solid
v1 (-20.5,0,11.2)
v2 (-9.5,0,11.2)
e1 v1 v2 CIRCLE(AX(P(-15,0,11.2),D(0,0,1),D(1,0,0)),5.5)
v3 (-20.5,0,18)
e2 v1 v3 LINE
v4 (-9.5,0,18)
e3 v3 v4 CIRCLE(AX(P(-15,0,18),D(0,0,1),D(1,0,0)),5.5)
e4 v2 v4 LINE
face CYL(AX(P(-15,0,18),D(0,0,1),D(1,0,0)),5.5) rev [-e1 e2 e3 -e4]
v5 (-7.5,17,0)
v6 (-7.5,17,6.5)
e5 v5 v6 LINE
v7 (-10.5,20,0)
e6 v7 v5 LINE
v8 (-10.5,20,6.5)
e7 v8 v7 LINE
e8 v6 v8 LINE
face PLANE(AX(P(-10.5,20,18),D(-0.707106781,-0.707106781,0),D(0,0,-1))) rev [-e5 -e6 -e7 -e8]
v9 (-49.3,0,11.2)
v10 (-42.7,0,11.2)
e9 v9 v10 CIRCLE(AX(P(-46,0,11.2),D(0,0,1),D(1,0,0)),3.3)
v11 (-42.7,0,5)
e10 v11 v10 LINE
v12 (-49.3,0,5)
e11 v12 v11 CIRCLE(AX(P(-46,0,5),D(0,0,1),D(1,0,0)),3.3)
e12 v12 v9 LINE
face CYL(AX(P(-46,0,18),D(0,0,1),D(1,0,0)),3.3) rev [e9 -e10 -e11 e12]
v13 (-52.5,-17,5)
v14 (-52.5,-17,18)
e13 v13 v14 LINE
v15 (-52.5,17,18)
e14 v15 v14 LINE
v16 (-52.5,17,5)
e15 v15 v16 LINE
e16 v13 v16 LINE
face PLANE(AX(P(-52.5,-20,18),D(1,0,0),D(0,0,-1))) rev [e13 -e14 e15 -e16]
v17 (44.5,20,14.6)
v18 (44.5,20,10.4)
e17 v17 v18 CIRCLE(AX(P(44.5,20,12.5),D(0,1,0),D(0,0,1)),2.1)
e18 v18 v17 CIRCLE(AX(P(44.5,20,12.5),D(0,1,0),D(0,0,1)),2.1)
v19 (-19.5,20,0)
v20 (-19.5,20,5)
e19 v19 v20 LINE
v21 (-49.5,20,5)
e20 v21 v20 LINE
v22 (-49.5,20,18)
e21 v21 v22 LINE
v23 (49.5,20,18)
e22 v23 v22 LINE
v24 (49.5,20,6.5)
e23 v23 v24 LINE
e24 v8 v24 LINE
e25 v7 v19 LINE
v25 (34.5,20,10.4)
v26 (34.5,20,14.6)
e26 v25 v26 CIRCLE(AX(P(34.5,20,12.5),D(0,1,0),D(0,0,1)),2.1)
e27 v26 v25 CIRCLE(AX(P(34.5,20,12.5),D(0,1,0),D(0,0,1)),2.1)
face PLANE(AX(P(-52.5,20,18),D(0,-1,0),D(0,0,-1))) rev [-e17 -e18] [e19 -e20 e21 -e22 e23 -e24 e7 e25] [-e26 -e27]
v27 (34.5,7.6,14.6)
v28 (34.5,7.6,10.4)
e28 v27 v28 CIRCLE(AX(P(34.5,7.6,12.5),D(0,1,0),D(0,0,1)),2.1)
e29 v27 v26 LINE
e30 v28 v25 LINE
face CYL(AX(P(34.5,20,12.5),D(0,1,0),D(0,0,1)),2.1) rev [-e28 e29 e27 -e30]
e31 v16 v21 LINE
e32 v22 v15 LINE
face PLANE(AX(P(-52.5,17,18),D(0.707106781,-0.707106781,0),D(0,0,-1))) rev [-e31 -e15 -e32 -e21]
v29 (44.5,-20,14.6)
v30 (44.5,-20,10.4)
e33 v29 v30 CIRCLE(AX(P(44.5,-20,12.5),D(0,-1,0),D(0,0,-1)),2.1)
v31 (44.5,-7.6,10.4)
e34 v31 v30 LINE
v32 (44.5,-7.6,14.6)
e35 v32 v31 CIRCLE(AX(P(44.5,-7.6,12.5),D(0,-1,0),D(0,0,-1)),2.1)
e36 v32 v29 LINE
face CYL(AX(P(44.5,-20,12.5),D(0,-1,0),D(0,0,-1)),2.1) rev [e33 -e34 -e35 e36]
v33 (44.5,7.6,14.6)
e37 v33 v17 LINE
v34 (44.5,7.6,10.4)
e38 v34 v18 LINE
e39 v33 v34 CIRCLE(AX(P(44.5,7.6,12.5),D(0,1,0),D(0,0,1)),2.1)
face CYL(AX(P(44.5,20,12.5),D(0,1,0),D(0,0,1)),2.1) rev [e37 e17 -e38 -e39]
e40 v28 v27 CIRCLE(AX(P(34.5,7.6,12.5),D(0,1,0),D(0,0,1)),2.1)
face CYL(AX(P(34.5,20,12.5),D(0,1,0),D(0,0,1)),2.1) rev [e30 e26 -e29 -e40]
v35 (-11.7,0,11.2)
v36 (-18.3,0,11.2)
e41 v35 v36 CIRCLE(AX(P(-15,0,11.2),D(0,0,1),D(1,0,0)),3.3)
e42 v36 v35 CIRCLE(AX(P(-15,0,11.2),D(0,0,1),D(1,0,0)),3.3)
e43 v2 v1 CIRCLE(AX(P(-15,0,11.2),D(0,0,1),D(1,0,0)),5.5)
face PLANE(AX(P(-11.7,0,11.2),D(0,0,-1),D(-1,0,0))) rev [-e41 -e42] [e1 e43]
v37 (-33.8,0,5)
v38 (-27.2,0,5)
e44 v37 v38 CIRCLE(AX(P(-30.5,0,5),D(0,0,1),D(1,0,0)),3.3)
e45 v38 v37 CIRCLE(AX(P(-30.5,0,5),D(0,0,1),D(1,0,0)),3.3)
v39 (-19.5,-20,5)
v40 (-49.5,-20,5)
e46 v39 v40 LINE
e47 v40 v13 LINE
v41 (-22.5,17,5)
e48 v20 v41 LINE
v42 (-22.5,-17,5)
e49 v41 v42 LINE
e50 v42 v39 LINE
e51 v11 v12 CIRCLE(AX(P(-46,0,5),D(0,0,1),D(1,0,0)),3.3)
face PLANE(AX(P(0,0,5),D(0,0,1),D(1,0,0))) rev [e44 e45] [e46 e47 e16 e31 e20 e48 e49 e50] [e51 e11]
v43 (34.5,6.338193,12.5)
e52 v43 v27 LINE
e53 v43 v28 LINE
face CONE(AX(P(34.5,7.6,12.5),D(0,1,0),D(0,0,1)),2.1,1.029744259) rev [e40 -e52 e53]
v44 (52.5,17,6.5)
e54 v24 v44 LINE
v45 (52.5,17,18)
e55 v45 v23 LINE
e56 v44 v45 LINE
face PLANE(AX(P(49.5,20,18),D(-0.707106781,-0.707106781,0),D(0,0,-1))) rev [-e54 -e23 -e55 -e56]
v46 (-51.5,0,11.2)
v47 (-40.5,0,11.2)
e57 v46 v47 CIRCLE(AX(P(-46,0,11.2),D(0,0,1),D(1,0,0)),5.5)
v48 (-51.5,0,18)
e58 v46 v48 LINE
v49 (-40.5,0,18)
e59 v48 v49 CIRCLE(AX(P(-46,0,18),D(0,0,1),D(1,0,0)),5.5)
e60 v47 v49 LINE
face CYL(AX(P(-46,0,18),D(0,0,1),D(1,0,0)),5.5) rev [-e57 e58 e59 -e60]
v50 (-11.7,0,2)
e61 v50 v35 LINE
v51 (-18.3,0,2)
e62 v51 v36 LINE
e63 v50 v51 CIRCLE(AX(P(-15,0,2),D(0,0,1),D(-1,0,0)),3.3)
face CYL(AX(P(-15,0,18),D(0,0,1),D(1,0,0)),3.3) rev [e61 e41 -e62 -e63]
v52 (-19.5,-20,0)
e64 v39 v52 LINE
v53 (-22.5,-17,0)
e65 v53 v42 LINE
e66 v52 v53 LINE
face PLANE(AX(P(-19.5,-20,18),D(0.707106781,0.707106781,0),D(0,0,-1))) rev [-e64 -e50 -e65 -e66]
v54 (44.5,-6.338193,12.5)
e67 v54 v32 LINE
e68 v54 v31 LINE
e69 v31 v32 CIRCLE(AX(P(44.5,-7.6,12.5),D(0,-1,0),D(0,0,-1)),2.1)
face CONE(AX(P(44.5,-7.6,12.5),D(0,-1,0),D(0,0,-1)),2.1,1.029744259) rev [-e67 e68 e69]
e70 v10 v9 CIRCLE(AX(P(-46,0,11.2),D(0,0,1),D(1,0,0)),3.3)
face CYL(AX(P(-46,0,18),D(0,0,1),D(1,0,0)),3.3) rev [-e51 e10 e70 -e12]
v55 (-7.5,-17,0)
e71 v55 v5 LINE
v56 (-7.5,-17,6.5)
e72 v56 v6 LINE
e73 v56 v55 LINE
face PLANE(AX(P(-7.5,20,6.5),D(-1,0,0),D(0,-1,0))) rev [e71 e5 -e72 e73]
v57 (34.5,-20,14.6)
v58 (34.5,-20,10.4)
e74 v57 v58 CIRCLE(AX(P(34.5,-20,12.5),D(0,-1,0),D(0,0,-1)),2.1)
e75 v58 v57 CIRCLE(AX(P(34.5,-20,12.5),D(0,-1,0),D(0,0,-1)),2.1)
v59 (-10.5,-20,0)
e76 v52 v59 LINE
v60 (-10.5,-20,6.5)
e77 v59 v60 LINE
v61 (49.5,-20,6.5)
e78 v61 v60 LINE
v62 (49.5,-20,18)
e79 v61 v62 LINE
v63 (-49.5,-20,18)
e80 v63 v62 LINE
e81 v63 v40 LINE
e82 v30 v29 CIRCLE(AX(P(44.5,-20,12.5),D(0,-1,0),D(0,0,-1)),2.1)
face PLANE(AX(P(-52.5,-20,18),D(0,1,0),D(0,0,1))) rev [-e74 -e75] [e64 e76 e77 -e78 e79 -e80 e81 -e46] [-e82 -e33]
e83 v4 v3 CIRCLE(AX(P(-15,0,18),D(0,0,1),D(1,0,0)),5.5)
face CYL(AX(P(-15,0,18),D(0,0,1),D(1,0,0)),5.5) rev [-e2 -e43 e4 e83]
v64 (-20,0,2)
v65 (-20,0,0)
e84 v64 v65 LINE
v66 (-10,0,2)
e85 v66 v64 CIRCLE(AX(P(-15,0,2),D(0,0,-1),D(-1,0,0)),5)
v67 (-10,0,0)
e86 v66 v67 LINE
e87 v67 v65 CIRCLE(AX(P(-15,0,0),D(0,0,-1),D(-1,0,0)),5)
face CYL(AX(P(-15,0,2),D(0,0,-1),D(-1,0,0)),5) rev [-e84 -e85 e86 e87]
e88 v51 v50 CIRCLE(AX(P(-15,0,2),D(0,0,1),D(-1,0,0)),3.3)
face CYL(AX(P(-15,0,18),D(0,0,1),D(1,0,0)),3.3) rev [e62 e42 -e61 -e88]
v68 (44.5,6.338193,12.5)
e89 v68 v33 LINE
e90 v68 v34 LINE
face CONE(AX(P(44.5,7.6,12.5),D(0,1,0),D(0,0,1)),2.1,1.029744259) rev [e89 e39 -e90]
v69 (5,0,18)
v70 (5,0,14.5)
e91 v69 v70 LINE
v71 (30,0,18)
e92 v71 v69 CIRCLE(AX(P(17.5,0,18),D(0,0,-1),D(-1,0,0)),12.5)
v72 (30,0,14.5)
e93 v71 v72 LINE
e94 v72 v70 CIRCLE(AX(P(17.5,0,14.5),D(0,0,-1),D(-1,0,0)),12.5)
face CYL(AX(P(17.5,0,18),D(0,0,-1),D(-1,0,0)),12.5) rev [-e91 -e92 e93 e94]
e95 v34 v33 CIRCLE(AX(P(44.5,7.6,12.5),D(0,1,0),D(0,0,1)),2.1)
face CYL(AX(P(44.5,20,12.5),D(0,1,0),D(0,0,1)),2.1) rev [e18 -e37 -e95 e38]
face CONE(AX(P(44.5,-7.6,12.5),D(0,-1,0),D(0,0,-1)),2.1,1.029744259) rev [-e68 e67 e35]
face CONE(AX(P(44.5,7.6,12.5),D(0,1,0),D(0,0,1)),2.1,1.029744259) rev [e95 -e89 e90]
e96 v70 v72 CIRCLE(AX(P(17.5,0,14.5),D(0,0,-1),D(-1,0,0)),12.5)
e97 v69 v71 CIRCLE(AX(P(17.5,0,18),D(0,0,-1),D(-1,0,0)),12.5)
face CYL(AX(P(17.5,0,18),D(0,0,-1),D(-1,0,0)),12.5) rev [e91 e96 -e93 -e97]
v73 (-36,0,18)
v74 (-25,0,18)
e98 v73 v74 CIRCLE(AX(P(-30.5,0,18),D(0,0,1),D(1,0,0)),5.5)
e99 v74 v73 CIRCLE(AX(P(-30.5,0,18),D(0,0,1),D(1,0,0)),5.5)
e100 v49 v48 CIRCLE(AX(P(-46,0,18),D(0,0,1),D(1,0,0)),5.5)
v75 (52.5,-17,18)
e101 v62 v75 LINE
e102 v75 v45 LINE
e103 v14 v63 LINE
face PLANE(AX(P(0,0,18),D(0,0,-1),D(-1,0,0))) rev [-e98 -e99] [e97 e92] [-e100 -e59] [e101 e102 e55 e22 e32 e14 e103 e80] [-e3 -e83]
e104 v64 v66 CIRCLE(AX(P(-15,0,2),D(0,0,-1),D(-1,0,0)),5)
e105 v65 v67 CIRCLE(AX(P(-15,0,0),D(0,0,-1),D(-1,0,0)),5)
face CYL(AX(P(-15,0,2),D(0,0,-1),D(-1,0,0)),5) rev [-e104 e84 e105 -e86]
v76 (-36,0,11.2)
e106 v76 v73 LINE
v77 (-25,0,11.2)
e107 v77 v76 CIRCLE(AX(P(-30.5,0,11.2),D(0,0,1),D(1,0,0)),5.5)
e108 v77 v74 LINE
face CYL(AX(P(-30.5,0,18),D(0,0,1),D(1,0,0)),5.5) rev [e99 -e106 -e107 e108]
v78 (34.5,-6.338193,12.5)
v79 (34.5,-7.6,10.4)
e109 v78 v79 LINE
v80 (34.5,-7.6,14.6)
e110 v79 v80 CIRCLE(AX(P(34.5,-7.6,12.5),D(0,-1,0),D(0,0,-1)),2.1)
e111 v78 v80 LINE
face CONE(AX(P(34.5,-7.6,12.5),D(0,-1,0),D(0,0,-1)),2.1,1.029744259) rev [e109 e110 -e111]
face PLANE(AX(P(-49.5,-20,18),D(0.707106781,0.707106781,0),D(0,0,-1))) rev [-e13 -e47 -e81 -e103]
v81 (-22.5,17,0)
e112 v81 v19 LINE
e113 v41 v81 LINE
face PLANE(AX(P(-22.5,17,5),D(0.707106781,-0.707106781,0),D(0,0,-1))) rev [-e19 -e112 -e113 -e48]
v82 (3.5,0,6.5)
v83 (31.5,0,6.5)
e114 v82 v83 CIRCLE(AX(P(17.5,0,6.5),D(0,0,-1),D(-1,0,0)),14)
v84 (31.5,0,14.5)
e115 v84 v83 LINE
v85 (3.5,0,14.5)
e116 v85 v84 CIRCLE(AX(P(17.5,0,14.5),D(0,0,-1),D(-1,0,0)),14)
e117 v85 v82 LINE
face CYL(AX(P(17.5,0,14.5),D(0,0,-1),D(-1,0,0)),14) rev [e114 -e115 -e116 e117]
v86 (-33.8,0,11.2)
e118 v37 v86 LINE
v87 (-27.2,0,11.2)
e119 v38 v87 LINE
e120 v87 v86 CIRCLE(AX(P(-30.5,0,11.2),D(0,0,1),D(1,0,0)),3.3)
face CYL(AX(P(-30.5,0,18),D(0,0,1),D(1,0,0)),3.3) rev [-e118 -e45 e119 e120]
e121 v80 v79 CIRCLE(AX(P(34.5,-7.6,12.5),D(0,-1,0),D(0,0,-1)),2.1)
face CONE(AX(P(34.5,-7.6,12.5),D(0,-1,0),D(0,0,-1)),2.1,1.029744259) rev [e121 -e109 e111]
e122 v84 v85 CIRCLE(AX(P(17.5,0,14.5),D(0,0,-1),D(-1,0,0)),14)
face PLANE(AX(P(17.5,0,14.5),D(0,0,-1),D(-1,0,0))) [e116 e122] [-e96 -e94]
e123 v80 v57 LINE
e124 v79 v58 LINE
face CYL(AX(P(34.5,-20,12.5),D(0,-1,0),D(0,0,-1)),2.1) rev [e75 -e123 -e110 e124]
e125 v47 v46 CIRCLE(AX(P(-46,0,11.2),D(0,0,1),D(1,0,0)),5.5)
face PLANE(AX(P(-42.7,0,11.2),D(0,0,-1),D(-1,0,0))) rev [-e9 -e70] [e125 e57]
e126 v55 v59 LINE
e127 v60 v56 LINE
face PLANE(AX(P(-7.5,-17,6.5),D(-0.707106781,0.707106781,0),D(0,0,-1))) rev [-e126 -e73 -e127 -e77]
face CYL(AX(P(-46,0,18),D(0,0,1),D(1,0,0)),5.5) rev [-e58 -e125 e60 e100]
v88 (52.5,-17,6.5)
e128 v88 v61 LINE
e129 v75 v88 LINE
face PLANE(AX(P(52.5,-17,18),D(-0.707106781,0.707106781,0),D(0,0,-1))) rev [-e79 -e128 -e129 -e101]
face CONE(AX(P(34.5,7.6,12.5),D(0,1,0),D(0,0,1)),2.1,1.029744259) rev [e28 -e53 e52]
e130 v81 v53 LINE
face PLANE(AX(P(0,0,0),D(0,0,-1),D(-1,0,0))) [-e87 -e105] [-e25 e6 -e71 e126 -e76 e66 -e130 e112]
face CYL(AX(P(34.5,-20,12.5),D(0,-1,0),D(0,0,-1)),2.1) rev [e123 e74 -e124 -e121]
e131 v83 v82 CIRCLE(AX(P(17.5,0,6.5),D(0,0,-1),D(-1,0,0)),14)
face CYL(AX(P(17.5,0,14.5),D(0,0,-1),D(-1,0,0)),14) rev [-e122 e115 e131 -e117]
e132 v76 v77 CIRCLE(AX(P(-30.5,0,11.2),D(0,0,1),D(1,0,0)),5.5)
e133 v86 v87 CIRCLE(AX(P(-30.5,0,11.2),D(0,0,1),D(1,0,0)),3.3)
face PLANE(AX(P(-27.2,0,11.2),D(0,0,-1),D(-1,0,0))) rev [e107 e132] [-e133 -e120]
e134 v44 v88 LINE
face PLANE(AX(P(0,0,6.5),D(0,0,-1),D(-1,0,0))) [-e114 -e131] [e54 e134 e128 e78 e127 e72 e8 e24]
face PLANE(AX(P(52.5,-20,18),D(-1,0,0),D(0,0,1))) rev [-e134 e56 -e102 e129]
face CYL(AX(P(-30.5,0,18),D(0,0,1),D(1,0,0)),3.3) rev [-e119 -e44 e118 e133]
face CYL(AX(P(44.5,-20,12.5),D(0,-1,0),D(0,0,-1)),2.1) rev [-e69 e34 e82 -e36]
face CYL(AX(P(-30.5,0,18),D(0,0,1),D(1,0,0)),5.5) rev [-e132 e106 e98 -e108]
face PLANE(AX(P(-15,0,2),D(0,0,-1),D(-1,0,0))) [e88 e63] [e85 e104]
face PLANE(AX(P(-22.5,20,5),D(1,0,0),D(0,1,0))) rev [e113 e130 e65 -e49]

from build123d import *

# Parameters (mm, degrees)
SKETCH_1_W                  = 105
SKETCH_1_H                  = 40
EXTRUDE_1_DEPTH             = 18
SKETCH_2_W                  = 30
SKETCH_2_H                  = 40
CUT_EXTRUDE_1_DEPTH         = 5
SKETCH_3_W                  = 60
SKETCH_3_H                  = 40
CUT_EXTRUDE_2_DEPTH         = 6.5
HOLE_WIZARD_1_D             = 6.6
HOLE_WIZARD_1_CBORE_D       = 11
HOLE_WIZARD_1_CBORE_DEPTH   = 6.8
SKETCH_6_R                  = 5
CUT_EXTRUDE_3_DEPTH         = 2
SKETCH_7_R                  = 14
CUT_EXTRUDE_4_DEPTH         = 8
SKETCH_8_R                  = 12.5
CUT_EXTRUDE_5_DEPTH         = 59.021547722
CHAMFER_1_SIZE              = 3
HOLE_WIZARD_M5_1_AT_2_COUNT = 2
HOLE_WIZARD_M5_1_AT_2_PITCH = 10


with BuildPart() as part:
    # 草图1 → 凸台-拉伸1 (new body)
    with BuildSketch(Plane.XY):
        Rectangle(SKETCH_1_W, SKETCH_1_H)
    extrude(amount=EXTRUDE_1_DEPTH)

    # 草图2 → 切除-拉伸1 (cut)
    with BuildSketch(Plane(origin=(0, 0, 0), x_dir=(-1, 0, 0), z_dir=(0, 0, -1))):
        with Locations((37.5, 0)):
            Rectangle(SKETCH_2_W, SKETCH_2_H)
    extrude(amount=-CUT_EXTRUDE_1_DEPTH, mode=Mode.SUBTRACT)

    # 草图3 → 切除-拉伸2 (cut)
    with BuildSketch(Plane(origin=(0, 0, 0), x_dir=(-1, 0, 0), z_dir=(0, 0, -1))):
        with Locations((-22.5, 0)):
            Rectangle(SKETCH_3_W, SKETCH_3_H)
    extrude(amount=-CUT_EXTRUDE_2_DEPTH, mode=Mode.SUBTRACT)

    # 打孔尺寸(%根据)内六角圆柱头螺钉的类型1 (through all)
    with Locations(Plane.XY.offset(18)):
        with Locations((-46, 0), (-30.5, 0), (-15, 0)):
            CounterBoreHole(HOLE_WIZARD_1_D / 2, HOLE_WIZARD_1_CBORE_D / 2, HOLE_WIZARD_1_CBORE_DEPTH)

    # 草图6 → 切除-拉伸3 (cut)
    with BuildSketch(Plane(origin=(0, 0, 0), x_dir=(-1, 0, 0), z_dir=(0, 0, -1))):
        with Locations((15, 0)):
            Circle(SKETCH_6_R)
    extrude(amount=-CUT_EXTRUDE_3_DEPTH, mode=Mode.SUBTRACT)

    # 草图7 → 切除-拉伸4 (cut)
    with BuildSketch(Plane(origin=(0, 0, 6.5), x_dir=(-1, 0, 0), z_dir=(0, 0, -1))):
        with Locations((-17.5, 0)):
            Circle(SKETCH_7_R)
    extrude(amount=-CUT_EXTRUDE_4_DEPTH, mode=Mode.SUBTRACT)

    # 草图8 → 切除-拉伸5 (cut, through all)
    with BuildSketch(Plane(origin=(0, 0, 14.5), x_dir=(-1, 0, 0), z_dir=(0, 0, -1))):
        with Locations((-17.5, 0)):
            Circle(SKETCH_8_R)
    extrude(amount=-CUT_EXTRUDE_5_DEPTH, mode=Mode.SUBTRACT)

    # 倒角1
    chamfer_1_edges = [part.edges().sort_by_distance(p)[0] for p in [
        (-22.5, -20, 2.5),
        (-22.5, 20, 2.5),
        (-7.5, 20, 3.25),
        (-7.5, -20, 3.25),
        (52.5, -20, 12.25),
        (-52.5, -20, 11.5),
        (-52.5, 20, 11.5),
        (52.5, 20, 12.25),
    ]]
    chamfer(chamfer_1_edges, length=CHAMFER_1_SIZE)

    # 草图10 → M5 螺纹孔1 (revolve, cut)
    with BuildSketch(Plane(origin=(44.5, -20, 12.5), x_dir=(0, 0, -1), z_dir=(1, 0, 0))):
        Polygon((0, 0), (0, 13.6618073), (2.1, 12.4), (2.1, 0), align=None)
    hole_wizard_m5_1 = revolve(axis=Axis((44.5, -26.35, 12.5), (0, 1, 0)), mode=Mode.SUBTRACT)

    # M5 螺纹孔1 at 2: M5 螺纹孔1 ×2
    with Locations(*[(-i * HOLE_WIZARD_M5_1_AT_2_PITCH, 0, 0) for i in range(1, HOLE_WIZARD_M5_1_AT_2_COUNT)]):
        add(hole_wizard_m5_1, mode=Mode.SUBTRACT)

    # 镜向1: M5 螺纹孔1 across plane
    add(hole_wizard_m5_1.mirror(Plane.ZX), mode=Mode.SUBTRACT)

    # 镜向1 copy 1 sketch → 镜向1 copy 1 (revolve, cut)
    with BuildSketch(Plane(origin=(34.5, 20, 12.5), x_dir=(0, 0, -1), z_dir=(1, 0, 0))):
        Polygon((0, 0), (0, -13.6618073), (2.1, -12.4), (2.1, 0), align=None)
    revolve(axis=Axis((34.5, 26.35, 12.5), (0, 1, 0)), mode=Mode.SUBTRACT)


solid = part.part
